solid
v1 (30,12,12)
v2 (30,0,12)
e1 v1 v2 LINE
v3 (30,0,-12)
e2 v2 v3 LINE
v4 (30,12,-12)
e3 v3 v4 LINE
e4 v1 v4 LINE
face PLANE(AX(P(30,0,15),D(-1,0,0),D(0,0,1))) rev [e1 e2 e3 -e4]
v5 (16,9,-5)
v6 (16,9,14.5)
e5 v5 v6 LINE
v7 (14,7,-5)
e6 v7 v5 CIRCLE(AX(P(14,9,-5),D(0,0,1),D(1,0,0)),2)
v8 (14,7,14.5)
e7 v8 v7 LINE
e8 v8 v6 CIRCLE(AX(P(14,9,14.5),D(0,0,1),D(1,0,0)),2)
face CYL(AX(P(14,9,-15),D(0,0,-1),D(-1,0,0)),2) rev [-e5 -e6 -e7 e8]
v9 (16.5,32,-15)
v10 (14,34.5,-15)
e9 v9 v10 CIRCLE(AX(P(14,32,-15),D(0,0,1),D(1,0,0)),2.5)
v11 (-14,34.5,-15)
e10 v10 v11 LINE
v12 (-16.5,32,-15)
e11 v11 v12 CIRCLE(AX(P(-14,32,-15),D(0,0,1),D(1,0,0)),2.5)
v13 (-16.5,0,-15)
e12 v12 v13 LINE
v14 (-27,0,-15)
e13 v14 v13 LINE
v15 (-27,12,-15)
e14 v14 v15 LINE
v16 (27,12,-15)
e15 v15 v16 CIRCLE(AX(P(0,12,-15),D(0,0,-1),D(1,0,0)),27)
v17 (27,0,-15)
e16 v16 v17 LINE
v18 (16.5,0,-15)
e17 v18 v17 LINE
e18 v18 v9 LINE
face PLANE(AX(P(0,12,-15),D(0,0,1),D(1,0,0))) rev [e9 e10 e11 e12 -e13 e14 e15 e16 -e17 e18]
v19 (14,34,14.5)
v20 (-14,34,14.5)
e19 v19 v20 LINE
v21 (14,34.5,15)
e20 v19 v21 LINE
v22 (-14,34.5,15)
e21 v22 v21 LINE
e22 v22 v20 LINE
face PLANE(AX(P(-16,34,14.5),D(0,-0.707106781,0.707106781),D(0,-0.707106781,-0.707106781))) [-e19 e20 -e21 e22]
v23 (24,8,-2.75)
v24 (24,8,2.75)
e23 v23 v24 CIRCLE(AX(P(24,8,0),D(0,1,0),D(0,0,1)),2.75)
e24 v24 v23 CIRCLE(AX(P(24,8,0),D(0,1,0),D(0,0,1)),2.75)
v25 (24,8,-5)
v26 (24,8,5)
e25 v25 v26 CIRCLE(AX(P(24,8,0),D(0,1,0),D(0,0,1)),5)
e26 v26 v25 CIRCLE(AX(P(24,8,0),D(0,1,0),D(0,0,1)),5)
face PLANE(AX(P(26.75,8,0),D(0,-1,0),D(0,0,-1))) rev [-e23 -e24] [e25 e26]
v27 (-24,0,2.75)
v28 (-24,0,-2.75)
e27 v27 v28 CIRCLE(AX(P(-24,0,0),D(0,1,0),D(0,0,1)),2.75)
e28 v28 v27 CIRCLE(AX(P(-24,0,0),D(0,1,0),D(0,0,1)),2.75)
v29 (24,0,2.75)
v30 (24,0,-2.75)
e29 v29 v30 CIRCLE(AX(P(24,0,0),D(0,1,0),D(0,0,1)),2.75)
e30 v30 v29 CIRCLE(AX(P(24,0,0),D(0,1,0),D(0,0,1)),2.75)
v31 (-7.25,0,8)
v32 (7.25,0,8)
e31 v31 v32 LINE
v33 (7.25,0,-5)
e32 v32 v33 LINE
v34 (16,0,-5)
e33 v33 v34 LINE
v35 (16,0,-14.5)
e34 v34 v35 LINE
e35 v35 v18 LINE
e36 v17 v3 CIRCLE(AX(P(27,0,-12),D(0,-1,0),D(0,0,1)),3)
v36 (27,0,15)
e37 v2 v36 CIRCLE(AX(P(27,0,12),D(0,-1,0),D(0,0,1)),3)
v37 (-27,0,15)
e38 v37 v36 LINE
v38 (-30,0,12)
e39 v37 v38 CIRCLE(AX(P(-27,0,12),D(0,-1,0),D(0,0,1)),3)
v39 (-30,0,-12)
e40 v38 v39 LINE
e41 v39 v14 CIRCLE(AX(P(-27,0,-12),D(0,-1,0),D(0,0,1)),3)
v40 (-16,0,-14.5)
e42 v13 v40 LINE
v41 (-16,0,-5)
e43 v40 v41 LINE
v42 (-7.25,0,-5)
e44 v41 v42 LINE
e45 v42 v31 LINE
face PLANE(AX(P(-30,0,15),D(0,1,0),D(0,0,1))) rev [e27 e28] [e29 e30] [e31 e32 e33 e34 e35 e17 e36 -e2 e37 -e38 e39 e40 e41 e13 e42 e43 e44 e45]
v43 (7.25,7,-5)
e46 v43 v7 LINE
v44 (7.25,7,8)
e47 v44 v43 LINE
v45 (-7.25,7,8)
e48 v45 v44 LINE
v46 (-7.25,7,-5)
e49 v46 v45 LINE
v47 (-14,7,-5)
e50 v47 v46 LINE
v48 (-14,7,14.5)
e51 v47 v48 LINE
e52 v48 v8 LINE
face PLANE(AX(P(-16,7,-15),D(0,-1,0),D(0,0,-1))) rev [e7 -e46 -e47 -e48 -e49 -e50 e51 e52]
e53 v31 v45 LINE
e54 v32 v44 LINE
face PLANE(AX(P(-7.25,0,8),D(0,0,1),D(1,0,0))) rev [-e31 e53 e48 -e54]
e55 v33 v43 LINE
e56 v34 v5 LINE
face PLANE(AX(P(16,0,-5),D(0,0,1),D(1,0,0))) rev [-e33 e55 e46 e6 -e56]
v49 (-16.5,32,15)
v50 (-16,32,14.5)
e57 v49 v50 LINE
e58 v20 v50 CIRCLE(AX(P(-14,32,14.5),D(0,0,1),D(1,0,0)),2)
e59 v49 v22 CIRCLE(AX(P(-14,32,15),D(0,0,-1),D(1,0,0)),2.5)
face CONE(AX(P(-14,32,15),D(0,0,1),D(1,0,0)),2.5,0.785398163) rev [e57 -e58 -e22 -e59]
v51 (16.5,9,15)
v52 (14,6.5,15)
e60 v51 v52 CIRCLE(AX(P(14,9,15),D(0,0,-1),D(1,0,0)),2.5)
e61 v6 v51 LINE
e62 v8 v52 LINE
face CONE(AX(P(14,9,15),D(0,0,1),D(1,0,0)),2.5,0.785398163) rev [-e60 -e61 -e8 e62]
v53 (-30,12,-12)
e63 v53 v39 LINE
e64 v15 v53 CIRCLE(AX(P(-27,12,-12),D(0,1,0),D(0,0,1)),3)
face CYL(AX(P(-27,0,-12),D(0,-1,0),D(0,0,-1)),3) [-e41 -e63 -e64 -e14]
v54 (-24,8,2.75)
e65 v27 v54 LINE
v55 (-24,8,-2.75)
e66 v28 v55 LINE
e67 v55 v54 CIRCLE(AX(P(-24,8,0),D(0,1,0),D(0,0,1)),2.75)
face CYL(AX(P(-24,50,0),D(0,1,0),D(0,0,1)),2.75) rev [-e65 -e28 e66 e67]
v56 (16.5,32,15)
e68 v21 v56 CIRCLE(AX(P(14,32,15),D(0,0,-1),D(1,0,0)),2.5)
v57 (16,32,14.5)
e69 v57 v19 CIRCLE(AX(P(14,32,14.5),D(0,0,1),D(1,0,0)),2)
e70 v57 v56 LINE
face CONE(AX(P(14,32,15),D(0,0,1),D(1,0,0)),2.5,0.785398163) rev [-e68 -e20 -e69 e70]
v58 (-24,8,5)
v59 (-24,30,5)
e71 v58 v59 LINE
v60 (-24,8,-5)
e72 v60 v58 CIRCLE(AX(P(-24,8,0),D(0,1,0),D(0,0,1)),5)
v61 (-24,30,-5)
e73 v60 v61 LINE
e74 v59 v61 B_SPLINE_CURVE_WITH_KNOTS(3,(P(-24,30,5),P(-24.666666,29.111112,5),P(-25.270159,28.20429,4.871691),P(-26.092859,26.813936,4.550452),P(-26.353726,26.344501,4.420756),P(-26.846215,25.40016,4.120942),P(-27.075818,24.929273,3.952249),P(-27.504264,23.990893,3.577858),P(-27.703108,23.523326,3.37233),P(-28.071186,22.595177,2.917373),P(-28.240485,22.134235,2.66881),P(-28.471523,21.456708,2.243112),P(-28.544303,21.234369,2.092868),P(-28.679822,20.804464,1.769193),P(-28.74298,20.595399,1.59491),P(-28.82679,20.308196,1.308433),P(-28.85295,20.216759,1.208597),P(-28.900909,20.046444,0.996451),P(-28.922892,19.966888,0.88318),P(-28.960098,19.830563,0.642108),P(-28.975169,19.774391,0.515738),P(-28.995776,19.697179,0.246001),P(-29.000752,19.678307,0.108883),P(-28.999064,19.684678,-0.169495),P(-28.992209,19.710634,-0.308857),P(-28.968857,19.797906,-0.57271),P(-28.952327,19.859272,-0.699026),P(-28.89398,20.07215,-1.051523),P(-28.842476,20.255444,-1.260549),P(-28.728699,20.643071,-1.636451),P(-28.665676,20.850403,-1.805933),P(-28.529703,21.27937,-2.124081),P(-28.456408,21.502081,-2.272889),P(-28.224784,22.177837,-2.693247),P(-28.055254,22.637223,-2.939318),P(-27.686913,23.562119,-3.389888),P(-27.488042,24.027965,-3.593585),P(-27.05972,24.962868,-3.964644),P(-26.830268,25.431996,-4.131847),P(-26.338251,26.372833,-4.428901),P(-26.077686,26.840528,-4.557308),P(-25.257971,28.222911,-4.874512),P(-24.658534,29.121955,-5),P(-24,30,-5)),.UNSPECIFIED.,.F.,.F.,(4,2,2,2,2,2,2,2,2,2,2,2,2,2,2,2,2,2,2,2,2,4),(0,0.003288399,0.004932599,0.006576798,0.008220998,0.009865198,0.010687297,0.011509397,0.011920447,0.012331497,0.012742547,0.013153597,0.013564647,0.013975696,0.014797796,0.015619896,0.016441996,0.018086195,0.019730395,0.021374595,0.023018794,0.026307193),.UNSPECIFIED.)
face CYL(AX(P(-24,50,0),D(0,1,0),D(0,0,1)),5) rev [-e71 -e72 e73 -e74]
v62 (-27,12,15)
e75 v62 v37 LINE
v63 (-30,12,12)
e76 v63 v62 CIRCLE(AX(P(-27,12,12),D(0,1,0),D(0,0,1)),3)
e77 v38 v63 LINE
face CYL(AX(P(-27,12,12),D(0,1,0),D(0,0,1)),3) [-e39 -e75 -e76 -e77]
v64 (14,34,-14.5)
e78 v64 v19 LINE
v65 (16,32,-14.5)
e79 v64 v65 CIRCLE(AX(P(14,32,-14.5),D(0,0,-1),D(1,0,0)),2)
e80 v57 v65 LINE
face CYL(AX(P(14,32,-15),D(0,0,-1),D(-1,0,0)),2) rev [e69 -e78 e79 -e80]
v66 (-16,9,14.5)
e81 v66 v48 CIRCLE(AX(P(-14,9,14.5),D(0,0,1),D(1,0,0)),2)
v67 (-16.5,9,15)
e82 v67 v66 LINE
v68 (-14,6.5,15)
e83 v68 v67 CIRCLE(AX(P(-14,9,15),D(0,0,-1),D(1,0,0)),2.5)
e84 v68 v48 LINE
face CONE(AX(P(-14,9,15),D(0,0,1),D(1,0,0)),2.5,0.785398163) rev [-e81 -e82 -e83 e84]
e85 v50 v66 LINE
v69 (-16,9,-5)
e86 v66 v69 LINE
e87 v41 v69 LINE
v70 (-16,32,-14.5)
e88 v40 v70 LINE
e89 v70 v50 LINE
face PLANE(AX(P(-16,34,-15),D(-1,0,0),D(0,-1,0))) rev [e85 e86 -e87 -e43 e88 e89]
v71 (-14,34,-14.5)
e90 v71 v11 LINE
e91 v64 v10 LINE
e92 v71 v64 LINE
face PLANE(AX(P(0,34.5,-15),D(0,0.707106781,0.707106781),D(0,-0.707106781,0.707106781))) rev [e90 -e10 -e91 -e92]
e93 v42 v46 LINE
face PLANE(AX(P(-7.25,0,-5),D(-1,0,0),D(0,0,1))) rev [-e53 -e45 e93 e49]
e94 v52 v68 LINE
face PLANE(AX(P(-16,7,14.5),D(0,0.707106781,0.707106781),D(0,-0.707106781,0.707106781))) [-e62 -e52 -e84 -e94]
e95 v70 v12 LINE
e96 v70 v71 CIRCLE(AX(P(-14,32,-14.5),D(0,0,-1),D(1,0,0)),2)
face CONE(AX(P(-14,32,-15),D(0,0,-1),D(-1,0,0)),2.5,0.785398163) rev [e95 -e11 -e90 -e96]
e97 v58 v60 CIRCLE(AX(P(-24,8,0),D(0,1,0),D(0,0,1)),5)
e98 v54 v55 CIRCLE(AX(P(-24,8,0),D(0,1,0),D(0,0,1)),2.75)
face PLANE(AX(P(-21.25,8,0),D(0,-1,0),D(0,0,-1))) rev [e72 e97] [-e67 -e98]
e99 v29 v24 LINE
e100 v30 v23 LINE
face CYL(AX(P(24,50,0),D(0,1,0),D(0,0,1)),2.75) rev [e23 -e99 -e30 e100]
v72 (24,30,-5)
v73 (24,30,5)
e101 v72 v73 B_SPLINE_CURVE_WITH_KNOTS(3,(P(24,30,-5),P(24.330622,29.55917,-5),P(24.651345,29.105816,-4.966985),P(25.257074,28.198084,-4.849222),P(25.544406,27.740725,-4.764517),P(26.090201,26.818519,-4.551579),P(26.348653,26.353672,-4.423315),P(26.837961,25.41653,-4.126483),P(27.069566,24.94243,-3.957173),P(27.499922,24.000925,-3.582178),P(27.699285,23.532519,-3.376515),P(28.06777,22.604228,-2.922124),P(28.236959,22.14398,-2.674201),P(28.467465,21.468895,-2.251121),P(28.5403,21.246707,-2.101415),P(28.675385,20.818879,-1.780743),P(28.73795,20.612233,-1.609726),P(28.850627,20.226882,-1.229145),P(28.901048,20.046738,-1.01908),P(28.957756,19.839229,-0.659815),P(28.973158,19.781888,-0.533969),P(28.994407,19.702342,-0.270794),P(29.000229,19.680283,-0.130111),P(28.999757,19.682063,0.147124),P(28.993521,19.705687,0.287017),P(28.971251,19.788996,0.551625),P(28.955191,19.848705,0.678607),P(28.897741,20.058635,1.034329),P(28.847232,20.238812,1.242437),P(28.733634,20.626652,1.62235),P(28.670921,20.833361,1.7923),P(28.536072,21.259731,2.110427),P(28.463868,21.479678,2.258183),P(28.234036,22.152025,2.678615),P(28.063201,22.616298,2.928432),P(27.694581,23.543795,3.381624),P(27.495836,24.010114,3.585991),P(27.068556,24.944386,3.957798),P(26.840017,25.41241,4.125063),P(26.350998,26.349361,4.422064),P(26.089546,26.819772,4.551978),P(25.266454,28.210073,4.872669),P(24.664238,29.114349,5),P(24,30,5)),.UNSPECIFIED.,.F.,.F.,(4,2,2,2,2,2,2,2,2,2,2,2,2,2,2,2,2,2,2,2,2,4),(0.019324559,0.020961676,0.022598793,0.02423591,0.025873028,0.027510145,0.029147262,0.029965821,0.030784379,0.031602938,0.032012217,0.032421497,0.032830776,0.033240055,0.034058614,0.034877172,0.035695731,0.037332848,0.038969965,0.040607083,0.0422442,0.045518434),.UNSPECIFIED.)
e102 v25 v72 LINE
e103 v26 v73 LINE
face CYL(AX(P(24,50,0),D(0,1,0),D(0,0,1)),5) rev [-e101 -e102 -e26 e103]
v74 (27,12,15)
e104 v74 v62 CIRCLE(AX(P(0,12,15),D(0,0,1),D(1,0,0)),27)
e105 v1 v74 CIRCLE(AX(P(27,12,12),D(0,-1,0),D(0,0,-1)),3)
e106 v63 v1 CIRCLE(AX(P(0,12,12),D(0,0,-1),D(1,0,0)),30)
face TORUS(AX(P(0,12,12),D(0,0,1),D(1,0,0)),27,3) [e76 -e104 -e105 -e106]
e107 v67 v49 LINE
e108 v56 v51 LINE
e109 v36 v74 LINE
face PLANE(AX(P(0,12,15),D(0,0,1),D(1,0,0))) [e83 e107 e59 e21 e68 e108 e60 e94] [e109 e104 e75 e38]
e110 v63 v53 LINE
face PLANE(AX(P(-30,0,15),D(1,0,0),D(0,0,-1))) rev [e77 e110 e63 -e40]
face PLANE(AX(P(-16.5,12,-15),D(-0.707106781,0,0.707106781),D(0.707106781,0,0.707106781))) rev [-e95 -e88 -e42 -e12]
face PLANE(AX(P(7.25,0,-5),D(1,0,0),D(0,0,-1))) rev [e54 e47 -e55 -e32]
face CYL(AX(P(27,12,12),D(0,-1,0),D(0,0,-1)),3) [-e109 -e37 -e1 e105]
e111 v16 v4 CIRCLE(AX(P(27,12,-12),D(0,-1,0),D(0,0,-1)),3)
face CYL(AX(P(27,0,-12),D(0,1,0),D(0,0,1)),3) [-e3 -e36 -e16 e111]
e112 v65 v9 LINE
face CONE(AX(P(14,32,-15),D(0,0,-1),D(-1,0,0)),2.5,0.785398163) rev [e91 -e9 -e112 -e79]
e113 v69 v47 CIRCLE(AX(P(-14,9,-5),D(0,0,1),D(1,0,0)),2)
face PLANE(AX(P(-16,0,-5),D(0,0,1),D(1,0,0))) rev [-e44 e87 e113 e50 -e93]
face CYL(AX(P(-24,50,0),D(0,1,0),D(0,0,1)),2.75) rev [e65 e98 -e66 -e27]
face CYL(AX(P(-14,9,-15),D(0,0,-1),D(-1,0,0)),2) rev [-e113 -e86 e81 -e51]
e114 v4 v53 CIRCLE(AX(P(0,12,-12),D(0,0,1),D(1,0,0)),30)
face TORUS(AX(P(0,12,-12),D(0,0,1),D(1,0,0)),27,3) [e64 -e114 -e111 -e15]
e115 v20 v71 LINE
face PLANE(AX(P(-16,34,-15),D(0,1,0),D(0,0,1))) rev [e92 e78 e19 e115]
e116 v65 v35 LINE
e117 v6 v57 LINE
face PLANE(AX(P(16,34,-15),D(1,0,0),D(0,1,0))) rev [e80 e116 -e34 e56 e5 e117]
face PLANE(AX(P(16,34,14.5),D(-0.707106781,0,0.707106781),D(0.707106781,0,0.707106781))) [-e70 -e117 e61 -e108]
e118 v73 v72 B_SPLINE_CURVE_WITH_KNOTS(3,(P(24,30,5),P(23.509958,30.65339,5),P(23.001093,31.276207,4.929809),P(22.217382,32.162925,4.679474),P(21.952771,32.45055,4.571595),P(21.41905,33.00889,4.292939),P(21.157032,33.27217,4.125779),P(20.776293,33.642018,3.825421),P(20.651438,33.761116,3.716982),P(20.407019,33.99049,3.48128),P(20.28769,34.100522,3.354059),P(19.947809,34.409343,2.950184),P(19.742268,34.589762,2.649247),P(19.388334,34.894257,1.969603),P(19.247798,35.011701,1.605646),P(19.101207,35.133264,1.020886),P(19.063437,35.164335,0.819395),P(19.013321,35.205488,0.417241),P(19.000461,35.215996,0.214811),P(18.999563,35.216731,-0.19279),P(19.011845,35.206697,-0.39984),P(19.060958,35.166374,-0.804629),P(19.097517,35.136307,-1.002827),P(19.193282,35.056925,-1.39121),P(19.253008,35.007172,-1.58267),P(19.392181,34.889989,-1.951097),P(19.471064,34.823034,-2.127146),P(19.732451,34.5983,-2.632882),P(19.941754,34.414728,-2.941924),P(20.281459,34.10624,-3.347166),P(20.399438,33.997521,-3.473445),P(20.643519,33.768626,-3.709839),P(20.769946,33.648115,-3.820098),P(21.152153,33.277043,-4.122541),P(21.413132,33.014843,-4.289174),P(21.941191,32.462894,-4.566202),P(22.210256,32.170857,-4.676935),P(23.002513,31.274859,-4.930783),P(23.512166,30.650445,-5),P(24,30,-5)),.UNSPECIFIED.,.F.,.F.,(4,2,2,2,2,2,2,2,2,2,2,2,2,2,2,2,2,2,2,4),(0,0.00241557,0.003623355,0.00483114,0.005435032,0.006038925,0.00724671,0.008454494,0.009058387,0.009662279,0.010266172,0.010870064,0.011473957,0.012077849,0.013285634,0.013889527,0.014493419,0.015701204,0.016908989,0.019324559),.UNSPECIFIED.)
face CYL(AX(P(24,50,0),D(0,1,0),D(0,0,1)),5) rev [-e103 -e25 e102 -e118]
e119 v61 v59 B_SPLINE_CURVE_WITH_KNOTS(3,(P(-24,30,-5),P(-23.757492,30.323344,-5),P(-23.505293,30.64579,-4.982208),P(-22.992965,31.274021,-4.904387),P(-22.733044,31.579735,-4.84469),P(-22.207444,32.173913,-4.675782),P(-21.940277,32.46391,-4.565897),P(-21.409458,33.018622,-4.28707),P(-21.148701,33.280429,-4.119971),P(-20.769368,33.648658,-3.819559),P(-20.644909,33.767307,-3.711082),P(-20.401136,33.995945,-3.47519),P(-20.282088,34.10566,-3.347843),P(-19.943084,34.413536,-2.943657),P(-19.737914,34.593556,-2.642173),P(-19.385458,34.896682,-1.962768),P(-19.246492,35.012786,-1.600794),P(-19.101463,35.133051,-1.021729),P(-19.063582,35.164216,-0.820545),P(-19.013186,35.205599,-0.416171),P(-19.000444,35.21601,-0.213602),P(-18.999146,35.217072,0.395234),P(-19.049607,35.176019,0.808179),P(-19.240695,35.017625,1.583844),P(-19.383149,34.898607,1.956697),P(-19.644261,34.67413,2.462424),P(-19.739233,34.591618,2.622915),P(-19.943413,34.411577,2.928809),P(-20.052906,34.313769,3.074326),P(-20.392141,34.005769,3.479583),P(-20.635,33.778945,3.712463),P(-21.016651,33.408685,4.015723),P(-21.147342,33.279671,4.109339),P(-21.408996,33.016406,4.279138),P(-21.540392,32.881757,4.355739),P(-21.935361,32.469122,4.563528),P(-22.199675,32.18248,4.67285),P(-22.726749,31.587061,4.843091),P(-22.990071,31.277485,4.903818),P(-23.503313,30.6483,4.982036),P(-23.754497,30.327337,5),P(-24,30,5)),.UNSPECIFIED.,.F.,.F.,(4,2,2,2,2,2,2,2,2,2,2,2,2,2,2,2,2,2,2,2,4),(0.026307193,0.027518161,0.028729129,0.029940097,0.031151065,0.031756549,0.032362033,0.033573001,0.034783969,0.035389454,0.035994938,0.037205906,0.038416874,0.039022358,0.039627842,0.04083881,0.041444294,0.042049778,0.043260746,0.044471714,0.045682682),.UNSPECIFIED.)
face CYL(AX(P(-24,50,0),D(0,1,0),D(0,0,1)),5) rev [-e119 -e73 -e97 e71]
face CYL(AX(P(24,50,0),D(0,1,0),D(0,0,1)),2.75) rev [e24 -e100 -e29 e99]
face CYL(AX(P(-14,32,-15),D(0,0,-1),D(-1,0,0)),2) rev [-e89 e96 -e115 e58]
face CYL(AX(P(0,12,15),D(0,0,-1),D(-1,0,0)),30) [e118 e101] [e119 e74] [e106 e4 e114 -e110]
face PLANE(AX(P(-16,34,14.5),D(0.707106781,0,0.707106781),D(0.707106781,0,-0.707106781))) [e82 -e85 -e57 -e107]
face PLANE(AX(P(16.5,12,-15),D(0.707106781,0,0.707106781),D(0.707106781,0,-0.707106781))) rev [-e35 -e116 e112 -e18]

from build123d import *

# Parameters (mm, degrees)
EXTRUDE_1_DEPTH              = 15
HOLE_WIZARD_M5_1_D           = 5.5
HOLE_WIZARD_M5_1_CBORE_D     = 10
HOLE_WIZARD_M5_1_CBORE_DEPTH = 42
SKETCH_4_W                   = 32
SKETCH_4_H                   = 27
CUT_EXTRUDE_2_DEPTH          = 60.699246397
CUT_EXTRUDE_3_DEPTH          = 49.476798739
FILLET_1_R                   = 2
FILLET_2_R                   = 3
CHAMFER_1_SIZE               = 0.5


with BuildPart() as part:
    # 草圖1 → 伸長1 (new, symmetric)
    with BuildSketch(Plane.XY):
        with BuildLine():
            Line((-30, 0), (30, 0))
            Line((30, 0), (30, 12))
            ThreePointArc((30, 12), (0, 42), (-30, 12))
            Line((-30, 12), (-30, 0))
        make_face()
    extrude(amount=EXTRUDE_1_DEPTH, both=True)

    # M5 六角承窩頭蓋螺釘的柱孔1 (through all)
    with Locations(Plane(origin=(0, 50, 0), x_dir=(1, 0, 0), z_dir=(0, 1, 0))):
        with Locations((-24, 0), (24, 0)):
            CounterBoreHole(HOLE_WIZARD_M5_1_D / 2, HOLE_WIZARD_M5_1_CBORE_D / 2, HOLE_WIZARD_M5_1_CBORE_DEPTH)

    # 草圖4 → 伸長2 (cut, through all)
    with BuildSketch(Plane.XY.offset(15)):
        with Locations((0, 20.5)):
            Rectangle(SKETCH_4_W, SKETCH_4_H)
    extrude(amount=-CUT_EXTRUDE_2_DEPTH, mode=Mode.SUBTRACT)

    # 草圖5 → 伸長3 (cut, through all)
    with BuildSketch(Plane(origin=(0, 7, 0), x_dir=(1, 0, 0), z_dir=(0, 1, 0))):
        Polygon((-16, 15), (-16, 5), (-7.25, 5), (-7.25, -8), (7.25, -8), (7.25, 5), (16, 5), (16, 15), align=None)
    extrude(amount=-CUT_EXTRUDE_3_DEPTH, mode=Mode.SUBTRACT)

    # 圓角1
    fillet_1_edges = [part.edges().sort_by_distance(p)[0] for p in [
        (-16, 34, 0),
        (16, 34, 0),
        (16, 7, 5),
        (-16, 7, 5),
    ]]
    fillet(fillet_1_edges, radius=FILLET_1_R)

    # 圓角2
    fillet_2_edges = [part.edges().sort_by_distance(p)[0] for p in [
        (30, 6, 15),
        (0, 42, 15),
        (-30, 6, 15),
        (0, 42, -15),
        (30, 6, -15),
        (-30, 6, -15),
    ]]
    fillet(fillet_2_edges, radius=FILLET_2_R)

    # 導角1
    chamfer_1_edges = [part.edges().sort_by_distance(p)[0] for p in [
        (16, 16, -15),
        (16, 20.5, 15),
        (0, 7, 15),
        (-16, 20.5, 15),
        (-16, 16, -15),
        (0, 34, 15),
        (0, 34, -15),
        (15.414213562, 7.585786438, 15),
        (-15.414213562, 7.585786438, 15),
        (-15.414213562, 33.414213562, 15),
        (-15.414213562, 33.414213562, -15),
        (15.414213562, 33.414213562, 15),
        (15.414213562, 33.414213562, -15),
    ]]
    chamfer(chamfer_1_edges, length=CHAMFER_1_SIZE)


solid = part.part
